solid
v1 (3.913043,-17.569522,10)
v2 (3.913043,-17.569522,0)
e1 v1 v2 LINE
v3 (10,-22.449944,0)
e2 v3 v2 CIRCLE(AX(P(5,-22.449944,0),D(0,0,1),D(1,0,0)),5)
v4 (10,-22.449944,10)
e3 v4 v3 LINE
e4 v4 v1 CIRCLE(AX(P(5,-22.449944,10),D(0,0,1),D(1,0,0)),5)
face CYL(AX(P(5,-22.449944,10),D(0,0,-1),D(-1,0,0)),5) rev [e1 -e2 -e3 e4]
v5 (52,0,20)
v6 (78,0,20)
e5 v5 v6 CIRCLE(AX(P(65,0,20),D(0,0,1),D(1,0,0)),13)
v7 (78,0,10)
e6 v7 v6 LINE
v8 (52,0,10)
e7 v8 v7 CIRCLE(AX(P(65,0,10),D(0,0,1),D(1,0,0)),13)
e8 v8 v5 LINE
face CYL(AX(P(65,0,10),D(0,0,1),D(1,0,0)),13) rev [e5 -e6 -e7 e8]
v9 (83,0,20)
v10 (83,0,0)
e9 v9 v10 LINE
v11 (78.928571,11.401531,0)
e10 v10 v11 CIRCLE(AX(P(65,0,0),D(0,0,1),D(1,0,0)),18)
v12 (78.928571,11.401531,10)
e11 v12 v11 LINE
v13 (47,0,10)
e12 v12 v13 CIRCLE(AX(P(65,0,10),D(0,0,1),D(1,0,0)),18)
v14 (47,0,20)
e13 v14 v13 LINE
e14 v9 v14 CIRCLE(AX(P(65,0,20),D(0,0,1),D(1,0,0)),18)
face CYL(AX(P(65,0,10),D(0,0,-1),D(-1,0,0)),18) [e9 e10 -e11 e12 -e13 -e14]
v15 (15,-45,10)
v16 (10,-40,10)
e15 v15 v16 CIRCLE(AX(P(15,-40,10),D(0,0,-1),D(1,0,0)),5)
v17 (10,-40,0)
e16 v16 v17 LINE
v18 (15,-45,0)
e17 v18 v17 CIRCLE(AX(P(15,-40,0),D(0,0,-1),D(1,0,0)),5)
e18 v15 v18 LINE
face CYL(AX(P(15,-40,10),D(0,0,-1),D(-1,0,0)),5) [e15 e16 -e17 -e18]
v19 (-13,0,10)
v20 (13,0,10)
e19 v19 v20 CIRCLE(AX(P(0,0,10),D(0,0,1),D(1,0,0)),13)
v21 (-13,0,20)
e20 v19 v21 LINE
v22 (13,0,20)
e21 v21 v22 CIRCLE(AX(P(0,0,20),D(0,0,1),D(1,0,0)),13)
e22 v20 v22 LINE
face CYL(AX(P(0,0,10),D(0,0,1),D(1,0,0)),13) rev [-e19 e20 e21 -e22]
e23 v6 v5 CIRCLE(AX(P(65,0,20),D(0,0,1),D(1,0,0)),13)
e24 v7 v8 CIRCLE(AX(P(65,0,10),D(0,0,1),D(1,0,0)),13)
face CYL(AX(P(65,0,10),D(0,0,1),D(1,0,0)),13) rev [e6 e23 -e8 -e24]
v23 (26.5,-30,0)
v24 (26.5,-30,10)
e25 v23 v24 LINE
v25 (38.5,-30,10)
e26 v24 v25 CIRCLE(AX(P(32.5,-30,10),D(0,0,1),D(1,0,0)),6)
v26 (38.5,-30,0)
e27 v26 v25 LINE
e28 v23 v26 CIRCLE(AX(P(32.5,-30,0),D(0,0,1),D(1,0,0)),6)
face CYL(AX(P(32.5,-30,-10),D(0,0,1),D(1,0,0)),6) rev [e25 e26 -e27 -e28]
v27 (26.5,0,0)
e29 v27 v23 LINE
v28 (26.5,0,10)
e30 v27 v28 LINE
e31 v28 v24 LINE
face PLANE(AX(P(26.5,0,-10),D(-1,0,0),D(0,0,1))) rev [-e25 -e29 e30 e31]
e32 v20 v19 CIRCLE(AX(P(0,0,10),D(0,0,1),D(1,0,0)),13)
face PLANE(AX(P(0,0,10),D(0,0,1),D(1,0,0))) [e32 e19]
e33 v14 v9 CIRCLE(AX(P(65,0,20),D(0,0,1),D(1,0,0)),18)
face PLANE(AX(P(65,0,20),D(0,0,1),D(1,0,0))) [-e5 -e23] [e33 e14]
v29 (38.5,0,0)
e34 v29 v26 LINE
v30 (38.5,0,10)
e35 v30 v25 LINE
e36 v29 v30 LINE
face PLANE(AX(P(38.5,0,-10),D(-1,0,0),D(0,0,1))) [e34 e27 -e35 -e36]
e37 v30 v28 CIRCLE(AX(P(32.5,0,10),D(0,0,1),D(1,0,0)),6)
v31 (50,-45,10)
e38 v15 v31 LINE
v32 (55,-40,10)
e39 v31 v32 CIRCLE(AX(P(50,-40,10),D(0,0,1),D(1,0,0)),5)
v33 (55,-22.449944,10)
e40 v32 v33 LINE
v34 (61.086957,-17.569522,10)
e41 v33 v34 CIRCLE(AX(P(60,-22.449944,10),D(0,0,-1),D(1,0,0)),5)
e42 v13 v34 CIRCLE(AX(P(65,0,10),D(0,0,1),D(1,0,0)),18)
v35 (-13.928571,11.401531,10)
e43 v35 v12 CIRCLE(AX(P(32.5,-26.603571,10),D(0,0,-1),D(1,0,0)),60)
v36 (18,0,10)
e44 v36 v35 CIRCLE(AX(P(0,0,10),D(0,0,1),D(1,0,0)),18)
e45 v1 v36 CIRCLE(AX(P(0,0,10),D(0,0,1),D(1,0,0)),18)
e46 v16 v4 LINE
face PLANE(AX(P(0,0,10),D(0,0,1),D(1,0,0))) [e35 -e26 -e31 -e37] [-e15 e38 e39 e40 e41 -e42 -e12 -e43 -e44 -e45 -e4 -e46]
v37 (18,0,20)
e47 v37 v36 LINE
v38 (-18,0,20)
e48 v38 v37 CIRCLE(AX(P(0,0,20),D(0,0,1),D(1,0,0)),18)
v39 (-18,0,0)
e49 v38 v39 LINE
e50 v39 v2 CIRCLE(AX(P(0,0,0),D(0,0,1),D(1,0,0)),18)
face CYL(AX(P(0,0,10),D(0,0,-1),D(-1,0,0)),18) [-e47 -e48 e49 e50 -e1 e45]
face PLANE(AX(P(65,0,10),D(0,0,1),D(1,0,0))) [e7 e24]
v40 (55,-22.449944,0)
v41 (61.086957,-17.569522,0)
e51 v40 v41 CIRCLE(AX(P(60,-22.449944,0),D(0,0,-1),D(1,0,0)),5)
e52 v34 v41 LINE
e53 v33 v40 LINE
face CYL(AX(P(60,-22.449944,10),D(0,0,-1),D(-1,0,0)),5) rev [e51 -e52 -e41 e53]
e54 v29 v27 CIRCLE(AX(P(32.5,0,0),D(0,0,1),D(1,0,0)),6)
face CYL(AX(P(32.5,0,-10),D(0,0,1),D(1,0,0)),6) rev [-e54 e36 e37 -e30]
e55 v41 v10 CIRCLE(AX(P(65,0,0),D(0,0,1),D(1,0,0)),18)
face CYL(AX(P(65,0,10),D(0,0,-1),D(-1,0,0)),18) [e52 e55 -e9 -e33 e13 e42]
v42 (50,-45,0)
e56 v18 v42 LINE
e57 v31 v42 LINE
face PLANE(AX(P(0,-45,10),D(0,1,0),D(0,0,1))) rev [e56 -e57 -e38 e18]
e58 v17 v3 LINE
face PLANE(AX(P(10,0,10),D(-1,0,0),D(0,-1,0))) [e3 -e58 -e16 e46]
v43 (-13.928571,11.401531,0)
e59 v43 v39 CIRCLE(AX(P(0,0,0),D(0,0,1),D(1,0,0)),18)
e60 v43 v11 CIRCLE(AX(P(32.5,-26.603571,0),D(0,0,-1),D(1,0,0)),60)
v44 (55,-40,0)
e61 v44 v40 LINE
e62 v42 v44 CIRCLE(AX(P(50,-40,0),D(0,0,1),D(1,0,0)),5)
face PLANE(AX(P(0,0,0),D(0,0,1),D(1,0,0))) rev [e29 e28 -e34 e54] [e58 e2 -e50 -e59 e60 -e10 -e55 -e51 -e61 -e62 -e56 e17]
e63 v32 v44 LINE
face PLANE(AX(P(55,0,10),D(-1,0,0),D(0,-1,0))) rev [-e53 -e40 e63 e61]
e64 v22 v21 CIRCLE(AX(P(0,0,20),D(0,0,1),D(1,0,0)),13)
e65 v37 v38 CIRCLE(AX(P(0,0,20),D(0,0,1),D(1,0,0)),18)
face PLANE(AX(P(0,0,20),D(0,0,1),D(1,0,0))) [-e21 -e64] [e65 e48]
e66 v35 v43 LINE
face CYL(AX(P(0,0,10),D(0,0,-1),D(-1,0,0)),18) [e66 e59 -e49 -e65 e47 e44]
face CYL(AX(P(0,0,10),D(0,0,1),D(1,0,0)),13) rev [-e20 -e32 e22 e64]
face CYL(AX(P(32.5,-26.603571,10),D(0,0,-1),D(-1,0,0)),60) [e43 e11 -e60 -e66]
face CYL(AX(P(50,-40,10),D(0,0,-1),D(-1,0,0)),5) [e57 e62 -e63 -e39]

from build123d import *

# Parameters (mm, degrees)
LOBED_BASE_PLATE_DEPTH   = 10
ROUND_BOSSES_SKETCH_R    = 18
ROUND_BOSSES_2X_36_DEPTH = 10
BOSS_BORES_SKETCH_R      = 13
BOSS_BORES_2X_13_DEPTH   = 10
CENTER_SLOT_DEPTH        = 20


with BuildPart() as part:
    # Lobed Base Sketch → Lobed Base Plate (new body)
    with BuildSketch(Plane.XY):
        with BuildLine():
            Line((15, -45), (50, -45))
            ThreePointArc((50, -45), (53.535533906, -43.535533906), (55, -40))
            Line((55, -40), (55, -22.449944321))
            ThreePointArc((55, -22.449944321), (56.872283789, -18.548996833), (61.086956522, -17.569521642))
            ThreePointArc((61.086956522, -17.569521642), (80.32671412, -9.438847084), (78.928571429, 11.40153051))
            ThreePointArc((78.928571429, 11.40153051), (32.5, 33.396428811), (-13.928571429, 11.40153051))
            ThreePointArc((-13.928571429, 11.40153051), (-15.32671412, -9.438847084), (3.913043478, -17.569521642))
            ThreePointArc((3.913043478, -17.569521642), (8.127716211, -18.548996833), (10, -22.449944321))
            Line((10, -22.449944321), (10, -40))
            ThreePointArc((10, -40), (11.464466094, -43.535533906), (15, -45))
        make_face()
    extrude(amount=LOBED_BASE_PLATE_DEPTH)

    # Round Bosses Sketch → Round Bosses 2xØ36 (add)
    with BuildSketch(Plane.XY.offset(10)):
        with Locations(Location((0, 0, 0), (0, 0, 140.697224227))):
            Circle(ROUND_BOSSES_SKETCH_R)
        with Locations(Location((65, 0, 0), (0, 0, 257.444142201))):
            Circle(ROUND_BOSSES_SKETCH_R)
    extrude(amount=ROUND_BOSSES_2X_36_DEPTH)

    # Boss Bores Sketch → Boss Bores 2xØ13 (cut)
    with BuildSketch(Plane.XY.offset(20)):
        Circle(BOSS_BORES_SKETCH_R)
        with Locations((65, 0)):
            Circle(BOSS_BORES_SKETCH_R)
    extrude(amount=-BOSS_BORES_2X_13_DEPTH, mode=Mode.SUBTRACT)

    # Center Slot Sketch → Center Slot (cut)
    with BuildSketch(Plane.XY.offset(10)):
        with BuildLine():
            Line((26.5, 0), (26.5, -30))
            ThreePointArc((26.5, -30), (32.5, -36), (38.5, -30))
            Line((38.5, -30), (38.5, 0))
            ThreePointArc((38.5, 0), (32.5, 6), (26.5, 0))
        make_face()
    extrude(amount=-CENTER_SLOT_DEPTH, mode=Mode.SUBTRACT)


solid = part.part
